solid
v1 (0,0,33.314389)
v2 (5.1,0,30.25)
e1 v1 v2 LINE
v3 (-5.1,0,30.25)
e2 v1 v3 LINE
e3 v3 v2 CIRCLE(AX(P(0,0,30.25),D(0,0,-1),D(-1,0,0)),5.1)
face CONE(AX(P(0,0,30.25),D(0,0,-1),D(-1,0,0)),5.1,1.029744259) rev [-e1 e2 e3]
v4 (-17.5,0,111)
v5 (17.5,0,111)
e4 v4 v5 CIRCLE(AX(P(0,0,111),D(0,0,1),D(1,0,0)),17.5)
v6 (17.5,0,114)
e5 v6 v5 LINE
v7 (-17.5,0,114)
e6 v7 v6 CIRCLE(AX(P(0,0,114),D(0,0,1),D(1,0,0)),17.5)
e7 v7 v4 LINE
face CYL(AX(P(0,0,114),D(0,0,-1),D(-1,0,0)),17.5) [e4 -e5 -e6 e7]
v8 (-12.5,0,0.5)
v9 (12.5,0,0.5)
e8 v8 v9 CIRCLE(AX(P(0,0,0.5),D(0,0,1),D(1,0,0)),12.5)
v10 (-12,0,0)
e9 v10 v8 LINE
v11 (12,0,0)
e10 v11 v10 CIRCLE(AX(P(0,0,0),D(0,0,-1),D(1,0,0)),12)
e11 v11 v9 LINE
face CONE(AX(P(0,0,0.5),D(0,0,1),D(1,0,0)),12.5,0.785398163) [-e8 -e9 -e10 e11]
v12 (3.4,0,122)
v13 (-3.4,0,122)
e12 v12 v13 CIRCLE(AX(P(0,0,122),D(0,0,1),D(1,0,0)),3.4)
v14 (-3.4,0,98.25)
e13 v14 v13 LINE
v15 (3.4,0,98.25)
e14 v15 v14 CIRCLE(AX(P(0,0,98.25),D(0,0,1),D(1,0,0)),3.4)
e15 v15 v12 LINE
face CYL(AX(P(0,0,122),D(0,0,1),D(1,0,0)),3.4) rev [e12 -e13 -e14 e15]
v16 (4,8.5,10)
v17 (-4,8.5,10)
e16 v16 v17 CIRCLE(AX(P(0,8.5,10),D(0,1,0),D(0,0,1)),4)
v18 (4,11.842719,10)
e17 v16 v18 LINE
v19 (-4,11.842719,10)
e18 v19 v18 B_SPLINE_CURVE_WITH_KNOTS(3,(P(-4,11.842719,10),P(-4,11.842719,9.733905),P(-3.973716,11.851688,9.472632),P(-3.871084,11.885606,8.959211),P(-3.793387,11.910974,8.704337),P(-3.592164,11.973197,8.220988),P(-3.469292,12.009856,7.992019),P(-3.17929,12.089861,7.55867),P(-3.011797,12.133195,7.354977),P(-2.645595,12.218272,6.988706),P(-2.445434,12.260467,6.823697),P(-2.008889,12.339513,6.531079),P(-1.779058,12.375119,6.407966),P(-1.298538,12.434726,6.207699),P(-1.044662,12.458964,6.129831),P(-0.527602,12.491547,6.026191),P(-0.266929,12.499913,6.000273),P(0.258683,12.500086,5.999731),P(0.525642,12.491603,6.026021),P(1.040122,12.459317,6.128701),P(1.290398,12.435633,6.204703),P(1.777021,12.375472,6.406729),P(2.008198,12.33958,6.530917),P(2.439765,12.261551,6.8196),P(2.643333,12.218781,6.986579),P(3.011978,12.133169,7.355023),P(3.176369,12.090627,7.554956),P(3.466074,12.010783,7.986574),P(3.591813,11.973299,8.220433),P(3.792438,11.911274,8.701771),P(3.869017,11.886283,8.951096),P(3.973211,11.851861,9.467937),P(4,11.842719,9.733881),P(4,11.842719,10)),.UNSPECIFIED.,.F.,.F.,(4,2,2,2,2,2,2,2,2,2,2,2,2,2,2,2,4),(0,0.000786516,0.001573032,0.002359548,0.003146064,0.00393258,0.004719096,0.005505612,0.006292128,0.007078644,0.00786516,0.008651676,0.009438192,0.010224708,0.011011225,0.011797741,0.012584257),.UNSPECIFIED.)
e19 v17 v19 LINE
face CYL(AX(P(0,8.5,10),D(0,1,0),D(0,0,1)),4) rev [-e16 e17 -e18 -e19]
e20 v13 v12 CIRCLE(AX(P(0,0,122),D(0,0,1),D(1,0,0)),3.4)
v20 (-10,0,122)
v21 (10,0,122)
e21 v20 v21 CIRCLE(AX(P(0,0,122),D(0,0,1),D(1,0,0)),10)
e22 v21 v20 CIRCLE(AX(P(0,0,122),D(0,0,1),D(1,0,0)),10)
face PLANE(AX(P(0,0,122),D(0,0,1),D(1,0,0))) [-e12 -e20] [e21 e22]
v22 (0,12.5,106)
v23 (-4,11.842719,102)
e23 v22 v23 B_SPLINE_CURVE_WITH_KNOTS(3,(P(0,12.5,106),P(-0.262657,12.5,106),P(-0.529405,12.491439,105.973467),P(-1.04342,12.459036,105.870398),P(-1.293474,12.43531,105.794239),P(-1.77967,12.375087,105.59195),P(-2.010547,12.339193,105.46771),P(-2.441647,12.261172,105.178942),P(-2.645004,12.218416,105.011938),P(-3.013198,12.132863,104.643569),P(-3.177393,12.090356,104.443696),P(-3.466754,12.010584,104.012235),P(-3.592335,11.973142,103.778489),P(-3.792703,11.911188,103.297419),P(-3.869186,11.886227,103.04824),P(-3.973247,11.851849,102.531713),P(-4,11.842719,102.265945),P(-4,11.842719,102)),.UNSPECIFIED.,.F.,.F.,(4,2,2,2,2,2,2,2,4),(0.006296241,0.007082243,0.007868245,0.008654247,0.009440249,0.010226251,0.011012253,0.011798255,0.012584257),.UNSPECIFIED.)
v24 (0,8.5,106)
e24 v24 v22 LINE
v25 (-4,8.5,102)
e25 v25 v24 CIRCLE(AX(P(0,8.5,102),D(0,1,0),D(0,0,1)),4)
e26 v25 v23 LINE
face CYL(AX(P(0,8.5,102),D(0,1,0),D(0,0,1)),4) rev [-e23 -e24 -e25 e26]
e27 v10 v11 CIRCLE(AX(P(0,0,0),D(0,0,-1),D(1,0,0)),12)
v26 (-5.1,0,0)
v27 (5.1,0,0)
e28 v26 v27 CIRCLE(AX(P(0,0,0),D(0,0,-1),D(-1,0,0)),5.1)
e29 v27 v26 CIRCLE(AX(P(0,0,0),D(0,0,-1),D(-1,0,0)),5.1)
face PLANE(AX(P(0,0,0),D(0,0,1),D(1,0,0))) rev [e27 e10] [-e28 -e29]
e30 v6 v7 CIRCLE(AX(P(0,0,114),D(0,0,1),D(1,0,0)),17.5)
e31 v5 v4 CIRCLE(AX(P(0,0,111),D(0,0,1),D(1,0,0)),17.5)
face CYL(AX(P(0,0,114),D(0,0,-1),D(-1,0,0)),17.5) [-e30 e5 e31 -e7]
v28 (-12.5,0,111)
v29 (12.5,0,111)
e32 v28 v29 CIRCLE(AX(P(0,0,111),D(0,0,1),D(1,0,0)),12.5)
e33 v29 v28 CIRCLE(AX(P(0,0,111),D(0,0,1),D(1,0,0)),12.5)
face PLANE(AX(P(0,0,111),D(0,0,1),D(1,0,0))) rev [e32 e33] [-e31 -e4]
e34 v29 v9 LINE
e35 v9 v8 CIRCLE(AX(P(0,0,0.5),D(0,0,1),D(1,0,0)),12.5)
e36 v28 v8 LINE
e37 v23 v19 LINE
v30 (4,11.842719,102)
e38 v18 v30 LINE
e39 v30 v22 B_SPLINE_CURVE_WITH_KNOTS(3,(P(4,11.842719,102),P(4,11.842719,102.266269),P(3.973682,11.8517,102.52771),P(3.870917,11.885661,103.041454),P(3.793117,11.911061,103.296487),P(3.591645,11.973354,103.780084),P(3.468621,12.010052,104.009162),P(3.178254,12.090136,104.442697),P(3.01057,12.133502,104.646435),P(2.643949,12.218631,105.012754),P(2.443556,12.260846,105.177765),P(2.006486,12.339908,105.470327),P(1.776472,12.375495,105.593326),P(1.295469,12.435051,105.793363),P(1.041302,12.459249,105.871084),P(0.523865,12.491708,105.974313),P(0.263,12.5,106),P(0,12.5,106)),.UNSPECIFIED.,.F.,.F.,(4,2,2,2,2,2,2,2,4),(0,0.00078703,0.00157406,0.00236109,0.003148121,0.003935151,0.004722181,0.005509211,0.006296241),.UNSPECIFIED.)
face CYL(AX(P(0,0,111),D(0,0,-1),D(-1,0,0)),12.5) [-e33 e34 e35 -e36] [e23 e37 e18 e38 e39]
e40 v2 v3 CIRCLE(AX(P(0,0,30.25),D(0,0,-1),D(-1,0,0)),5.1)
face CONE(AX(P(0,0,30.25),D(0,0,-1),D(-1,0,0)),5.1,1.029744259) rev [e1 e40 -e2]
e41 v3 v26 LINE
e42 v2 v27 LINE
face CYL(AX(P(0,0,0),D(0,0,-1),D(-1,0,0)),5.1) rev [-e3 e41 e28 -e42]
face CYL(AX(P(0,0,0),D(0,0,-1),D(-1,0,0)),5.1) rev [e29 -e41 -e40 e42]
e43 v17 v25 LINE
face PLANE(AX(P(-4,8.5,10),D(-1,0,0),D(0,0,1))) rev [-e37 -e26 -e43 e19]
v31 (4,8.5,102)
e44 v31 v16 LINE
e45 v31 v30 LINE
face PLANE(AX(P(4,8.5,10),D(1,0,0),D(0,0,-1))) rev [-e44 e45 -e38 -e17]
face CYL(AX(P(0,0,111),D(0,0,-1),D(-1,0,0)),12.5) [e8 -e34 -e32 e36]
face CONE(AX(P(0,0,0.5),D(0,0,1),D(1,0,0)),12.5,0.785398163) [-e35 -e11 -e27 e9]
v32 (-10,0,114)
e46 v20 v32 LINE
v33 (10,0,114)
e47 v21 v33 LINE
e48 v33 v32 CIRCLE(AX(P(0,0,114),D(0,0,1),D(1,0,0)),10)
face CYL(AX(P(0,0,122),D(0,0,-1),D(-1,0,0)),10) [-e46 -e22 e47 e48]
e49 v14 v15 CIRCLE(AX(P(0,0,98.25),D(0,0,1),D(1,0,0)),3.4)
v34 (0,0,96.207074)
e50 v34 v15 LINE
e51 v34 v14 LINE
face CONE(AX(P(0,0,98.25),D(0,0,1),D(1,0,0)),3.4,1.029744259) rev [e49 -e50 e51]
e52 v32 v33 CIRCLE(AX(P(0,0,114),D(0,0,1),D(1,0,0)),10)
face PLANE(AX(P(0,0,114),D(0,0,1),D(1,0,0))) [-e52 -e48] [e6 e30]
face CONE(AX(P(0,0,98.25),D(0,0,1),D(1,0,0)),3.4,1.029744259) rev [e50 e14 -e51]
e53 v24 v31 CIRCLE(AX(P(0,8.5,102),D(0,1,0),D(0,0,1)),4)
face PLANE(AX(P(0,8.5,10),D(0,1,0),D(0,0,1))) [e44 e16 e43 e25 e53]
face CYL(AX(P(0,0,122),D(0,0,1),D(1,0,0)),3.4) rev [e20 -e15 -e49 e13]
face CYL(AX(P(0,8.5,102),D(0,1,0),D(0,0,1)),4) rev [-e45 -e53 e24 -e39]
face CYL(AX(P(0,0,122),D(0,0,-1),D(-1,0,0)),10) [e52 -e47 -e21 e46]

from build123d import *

# Parameters (mm, degrees)
SKETCH_1_R              = 12.5
EXTRUDE_1_DEPTH         = 111
SKETCH_2_R              = 17.5
EXTRUDE_2_DEPTH         = 3
SKETCH_3_R              = 10
EXTRUDE_3_DEPTH         = 8
CUT_EXTRUDE_1_DEPTH     = 4
HOLE_WIZARD_M8_1_D      = 6.8
HOLE_WIZARD_M8_1_DEPTH  = 23.75
HOLE_WIZARD_M8_1_TIP    = 2.042926105
HOLE_WIZARD_M12_1_D     = 10.2
HOLE_WIZARD_M12_1_DEPTH = 30.25
HOLE_WIZARD_M12_1_TIP   = 3.064389157
CHAMFER_1_SIZE          = 0.5


with BuildPart() as part:
    # 草图1 → 凸台-拉伸1 (new body)
    with BuildSketch(Plane.XY):
        Circle(SKETCH_1_R)
    extrude(amount=EXTRUDE_1_DEPTH)

    # 草图2 → 凸台-拉伸2 (add)
    with BuildSketch(Plane.XY.offset(111)):
        Circle(SKETCH_2_R)
    extrude(amount=EXTRUDE_2_DEPTH)

    # 草图3 → 凸台-拉伸3 (add)
    with BuildSketch(Plane.XY.offset(114)):
        Circle(SKETCH_3_R)
    extrude(amount=EXTRUDE_3_DEPTH)

    # 草图4 → 切除-拉伸1 (cut)
    with BuildSketch(Plane(origin=(0, 12.5, 0), x_dir=(1, 0, 0), z_dir=(0, 1, 0))):
        with BuildLine():
            Line((4, -10), (4, -102))
            ThreePointArc((4, -102), (0, -106), (-4, -102))
            Line((-4, -102), (-4, -10))
            ThreePointArc((-4, -10), (0, -6), (4, -10))
        make_face()
    extrude(amount=-CUT_EXTRUDE_1_DEPTH, mode=Mode.SUBTRACT)

    # M8 螺纹孔1
    with Locations(Plane.XY.offset(122)):
        with Locations((0, 0)):
            Hole(HOLE_WIZARD_M8_1_D / 2, depth=HOLE_WIZARD_M8_1_DEPTH)
            with Locations((0, 0, -(HOLE_WIZARD_M8_1_DEPTH + HOLE_WIZARD_M8_1_TIP / 2))):  # 118° drill point
                Cone(0, HOLE_WIZARD_M8_1_D / 2, HOLE_WIZARD_M8_1_TIP, mode=Mode.SUBTRACT)

    # M12 螺纹孔1
    with Locations(Plane(origin=(0, 0, 0), x_dir=(-1, 0, 0), z_dir=(0, 0, -1))):
        with Locations((0, 0)):
            Hole(HOLE_WIZARD_M12_1_D / 2, depth=HOLE_WIZARD_M12_1_DEPTH)
            with Locations((0, 0, -(HOLE_WIZARD_M12_1_DEPTH + HOLE_WIZARD_M12_1_TIP / 2))):  # 118° drill point
                Cone(0, HOLE_WIZARD_M12_1_D / 2, HOLE_WIZARD_M12_1_TIP, mode=Mode.SUBTRACT)

    # 倒角1
    chamfer_1_edges = [part.edges().sort_by_distance(p)[0] for p in [
        (-12.5, 0, 0),
    ]]
    chamfer(chamfer_1_edges, length=CHAMFER_1_SIZE)


solid = part.part
